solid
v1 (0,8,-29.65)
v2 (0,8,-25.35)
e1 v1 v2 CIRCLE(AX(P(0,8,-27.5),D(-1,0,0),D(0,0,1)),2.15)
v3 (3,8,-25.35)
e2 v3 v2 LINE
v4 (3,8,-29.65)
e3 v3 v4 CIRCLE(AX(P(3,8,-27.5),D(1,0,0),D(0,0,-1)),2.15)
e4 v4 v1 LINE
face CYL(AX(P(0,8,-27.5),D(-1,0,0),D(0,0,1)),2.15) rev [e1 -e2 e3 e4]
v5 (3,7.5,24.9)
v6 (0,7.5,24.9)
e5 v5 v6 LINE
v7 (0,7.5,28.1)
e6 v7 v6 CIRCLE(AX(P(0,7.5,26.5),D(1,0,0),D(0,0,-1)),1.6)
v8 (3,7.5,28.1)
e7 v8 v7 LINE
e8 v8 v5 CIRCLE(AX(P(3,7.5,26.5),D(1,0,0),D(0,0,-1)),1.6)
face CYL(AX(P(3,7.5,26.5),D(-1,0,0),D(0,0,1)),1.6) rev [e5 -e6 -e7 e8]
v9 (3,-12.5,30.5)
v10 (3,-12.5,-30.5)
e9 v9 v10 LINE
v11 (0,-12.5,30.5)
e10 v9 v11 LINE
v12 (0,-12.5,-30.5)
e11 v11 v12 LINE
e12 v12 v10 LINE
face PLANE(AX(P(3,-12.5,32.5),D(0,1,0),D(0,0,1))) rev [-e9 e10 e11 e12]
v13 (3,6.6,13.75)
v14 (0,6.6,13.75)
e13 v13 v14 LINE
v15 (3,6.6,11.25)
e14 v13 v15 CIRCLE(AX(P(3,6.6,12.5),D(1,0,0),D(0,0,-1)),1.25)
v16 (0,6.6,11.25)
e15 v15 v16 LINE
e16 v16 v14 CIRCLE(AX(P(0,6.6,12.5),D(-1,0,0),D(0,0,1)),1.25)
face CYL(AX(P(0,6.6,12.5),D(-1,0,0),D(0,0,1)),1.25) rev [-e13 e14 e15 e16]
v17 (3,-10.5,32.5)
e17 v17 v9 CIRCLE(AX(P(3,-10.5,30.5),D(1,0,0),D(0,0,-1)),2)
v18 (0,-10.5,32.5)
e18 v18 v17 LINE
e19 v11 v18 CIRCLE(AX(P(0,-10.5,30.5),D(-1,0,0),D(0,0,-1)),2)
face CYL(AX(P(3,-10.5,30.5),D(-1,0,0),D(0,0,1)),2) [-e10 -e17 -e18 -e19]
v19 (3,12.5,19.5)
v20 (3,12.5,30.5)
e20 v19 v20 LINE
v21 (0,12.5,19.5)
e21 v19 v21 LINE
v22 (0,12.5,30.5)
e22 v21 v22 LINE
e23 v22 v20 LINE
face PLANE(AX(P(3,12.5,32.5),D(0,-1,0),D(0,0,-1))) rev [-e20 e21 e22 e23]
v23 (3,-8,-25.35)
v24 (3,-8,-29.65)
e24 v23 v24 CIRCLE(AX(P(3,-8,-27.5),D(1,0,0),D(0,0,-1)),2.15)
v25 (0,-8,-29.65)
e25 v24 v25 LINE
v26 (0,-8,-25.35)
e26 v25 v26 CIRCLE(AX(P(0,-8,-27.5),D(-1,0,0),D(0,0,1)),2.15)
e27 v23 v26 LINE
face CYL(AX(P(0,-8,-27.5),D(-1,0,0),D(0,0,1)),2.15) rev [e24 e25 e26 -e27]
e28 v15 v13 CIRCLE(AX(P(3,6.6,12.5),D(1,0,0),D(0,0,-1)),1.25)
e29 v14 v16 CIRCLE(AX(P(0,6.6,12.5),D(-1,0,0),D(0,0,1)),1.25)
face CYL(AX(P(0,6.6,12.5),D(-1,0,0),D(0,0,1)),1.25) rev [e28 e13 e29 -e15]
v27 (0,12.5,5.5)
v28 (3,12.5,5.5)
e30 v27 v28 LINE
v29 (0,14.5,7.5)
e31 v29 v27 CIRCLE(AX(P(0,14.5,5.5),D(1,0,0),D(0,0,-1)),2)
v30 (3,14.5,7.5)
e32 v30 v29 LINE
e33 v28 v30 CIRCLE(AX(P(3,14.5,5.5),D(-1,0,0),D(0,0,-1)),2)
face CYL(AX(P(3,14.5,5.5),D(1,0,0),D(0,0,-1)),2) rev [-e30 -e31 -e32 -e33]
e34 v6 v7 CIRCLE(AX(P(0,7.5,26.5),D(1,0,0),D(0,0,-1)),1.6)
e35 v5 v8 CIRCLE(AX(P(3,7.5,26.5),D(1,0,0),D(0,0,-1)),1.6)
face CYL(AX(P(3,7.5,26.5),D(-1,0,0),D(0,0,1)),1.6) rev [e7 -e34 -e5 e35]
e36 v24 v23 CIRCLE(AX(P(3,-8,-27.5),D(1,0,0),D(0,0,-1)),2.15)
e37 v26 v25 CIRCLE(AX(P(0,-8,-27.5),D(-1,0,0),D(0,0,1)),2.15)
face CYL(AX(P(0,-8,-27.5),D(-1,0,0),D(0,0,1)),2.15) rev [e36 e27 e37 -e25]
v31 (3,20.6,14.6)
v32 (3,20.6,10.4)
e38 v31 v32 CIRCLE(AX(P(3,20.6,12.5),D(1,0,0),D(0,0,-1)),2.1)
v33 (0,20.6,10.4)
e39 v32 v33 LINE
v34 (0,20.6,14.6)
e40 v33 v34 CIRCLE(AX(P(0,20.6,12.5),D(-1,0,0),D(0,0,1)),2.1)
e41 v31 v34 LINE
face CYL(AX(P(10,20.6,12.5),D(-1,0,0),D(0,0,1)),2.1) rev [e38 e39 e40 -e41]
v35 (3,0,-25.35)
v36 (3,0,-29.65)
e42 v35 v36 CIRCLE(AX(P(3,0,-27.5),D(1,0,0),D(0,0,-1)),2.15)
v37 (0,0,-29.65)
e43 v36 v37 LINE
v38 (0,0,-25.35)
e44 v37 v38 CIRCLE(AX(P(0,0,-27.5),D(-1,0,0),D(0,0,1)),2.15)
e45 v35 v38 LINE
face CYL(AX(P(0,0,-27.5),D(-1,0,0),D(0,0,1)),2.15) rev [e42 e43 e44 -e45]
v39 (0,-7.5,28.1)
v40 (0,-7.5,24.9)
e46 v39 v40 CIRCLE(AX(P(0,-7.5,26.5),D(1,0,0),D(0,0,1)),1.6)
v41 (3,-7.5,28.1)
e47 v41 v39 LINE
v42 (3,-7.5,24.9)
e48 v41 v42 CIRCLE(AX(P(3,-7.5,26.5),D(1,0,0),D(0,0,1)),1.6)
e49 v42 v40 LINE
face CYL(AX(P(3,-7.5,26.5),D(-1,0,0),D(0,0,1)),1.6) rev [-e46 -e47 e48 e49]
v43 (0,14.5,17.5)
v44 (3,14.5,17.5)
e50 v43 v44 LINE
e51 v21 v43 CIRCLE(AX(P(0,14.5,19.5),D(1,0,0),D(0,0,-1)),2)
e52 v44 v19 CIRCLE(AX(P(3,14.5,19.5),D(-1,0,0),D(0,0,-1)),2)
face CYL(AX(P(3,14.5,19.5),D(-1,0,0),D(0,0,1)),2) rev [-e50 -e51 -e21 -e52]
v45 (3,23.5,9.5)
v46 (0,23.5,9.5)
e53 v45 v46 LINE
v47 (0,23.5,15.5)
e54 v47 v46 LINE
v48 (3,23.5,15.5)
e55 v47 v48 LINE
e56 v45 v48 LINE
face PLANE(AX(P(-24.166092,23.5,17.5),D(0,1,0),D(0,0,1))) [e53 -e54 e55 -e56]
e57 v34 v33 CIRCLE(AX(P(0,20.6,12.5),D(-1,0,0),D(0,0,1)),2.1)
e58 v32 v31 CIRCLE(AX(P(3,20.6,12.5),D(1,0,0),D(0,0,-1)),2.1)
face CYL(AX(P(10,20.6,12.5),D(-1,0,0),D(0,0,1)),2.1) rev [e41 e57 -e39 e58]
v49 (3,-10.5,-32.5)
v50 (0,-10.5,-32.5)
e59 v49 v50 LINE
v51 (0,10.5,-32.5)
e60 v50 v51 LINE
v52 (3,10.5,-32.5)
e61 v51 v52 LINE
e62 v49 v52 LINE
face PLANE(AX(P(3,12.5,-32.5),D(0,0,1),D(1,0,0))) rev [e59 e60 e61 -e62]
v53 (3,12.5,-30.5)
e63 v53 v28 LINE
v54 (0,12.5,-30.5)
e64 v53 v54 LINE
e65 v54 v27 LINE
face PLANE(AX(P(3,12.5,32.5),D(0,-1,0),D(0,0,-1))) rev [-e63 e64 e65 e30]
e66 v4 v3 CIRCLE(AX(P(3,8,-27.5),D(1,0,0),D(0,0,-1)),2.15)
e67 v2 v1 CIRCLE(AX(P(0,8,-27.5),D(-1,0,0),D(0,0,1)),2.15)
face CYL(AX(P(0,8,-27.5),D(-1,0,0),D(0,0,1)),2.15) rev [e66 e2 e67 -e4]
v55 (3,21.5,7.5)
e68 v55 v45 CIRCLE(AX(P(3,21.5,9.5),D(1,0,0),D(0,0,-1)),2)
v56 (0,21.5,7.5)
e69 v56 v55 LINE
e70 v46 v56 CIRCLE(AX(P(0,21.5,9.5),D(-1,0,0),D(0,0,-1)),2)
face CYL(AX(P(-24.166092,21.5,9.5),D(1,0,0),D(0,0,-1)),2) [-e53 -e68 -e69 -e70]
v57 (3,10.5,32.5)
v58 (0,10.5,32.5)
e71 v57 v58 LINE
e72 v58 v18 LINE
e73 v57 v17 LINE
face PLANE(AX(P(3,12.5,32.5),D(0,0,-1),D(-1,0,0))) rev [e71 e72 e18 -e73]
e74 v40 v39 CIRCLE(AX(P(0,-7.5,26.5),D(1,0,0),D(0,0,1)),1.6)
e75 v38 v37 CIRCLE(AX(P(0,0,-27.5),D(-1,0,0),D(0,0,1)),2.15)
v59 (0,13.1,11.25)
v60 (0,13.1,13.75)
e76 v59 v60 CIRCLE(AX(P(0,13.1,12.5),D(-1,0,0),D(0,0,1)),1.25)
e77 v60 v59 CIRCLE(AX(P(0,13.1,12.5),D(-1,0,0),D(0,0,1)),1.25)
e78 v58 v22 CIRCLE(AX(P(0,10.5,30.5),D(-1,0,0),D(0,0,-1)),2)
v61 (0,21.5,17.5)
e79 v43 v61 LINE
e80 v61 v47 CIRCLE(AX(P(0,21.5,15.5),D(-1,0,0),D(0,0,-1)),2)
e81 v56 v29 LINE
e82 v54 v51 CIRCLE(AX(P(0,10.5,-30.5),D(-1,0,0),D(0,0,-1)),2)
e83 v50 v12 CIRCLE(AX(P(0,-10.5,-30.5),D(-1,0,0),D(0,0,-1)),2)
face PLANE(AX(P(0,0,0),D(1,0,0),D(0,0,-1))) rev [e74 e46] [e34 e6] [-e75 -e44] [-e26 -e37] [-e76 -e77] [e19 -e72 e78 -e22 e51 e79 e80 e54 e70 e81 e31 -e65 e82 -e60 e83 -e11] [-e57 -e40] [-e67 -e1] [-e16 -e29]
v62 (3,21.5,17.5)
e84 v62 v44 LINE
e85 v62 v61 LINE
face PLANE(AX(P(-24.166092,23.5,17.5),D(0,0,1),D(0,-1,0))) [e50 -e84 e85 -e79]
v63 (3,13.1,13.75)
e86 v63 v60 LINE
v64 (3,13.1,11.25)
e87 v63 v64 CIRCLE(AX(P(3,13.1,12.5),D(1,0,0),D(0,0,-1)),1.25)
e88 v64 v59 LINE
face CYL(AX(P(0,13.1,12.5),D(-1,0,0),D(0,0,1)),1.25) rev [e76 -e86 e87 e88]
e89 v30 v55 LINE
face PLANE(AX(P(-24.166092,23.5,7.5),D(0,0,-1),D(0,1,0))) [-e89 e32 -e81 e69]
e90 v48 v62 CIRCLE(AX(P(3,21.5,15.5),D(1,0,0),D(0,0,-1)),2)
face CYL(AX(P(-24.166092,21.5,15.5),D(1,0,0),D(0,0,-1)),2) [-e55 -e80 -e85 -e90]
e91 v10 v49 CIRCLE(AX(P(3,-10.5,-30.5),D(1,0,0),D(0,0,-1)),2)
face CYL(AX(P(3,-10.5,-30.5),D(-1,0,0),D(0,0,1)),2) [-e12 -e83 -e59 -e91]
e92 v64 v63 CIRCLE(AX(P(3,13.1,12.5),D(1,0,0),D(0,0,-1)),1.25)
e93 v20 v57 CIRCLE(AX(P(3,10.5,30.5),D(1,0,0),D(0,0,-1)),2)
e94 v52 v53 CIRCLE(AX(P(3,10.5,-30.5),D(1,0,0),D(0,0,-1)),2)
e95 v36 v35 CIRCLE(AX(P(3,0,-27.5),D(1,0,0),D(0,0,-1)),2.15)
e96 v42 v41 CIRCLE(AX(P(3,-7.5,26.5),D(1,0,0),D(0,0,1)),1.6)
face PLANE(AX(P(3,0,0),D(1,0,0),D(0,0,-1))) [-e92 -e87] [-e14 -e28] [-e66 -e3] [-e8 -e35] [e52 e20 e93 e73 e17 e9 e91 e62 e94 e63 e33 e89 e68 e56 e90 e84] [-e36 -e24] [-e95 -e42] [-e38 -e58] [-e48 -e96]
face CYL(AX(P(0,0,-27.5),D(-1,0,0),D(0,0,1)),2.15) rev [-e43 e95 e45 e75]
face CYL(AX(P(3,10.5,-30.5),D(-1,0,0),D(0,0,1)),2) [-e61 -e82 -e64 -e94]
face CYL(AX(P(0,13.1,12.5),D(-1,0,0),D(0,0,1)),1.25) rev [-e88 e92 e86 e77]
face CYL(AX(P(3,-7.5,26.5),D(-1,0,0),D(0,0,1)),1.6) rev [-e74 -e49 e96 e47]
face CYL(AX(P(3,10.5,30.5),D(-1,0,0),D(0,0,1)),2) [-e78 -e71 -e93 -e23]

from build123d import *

# Parameters (mm, degrees)
SKETCH_1_W                  = 65
SKETCH_1_H                  = 25
SKETCH_1_R                  = 1.6
EXTRUDE_1_DEPTH             = 3
FILLET_1_R                  = 2
HOLE_WIZARD_4_3_4_3_1_D     = 4.3
HOLE_WIZARD_4_3_4_3_1_DEPTH = 11.5
HOLE_WIZARD_4_3_4_3_1_TIP   = 1.291850331
SKETCH_4_W                  = 10
SKETCH_4_H                  = 22
EXTRUDE_2_DEPTH             = 3
SKETCH_5_R                  = 2.1
CUT_EXTRUDE_1_DEPTH         = 10
FILLET_2_R                  = 2
HOLE_WIZARD_M3_1_D          = 2.5
HOLE_WIZARD_M3_1_DEPTH      = 8.5
HOLE_WIZARD_M3_1_TIP        = 0.751075774


with BuildPart() as part:
    # 草图1 → 凸台-拉伸1 (new body)
    with BuildSketch(Plane(origin=(0, 0, 0), x_dir=(0, 0, -1), z_dir=(1, 0, 0))):
        Rectangle(SKETCH_1_W, SKETCH_1_H)
        with Locations((-26.5, 7.5)):
            Circle(SKETCH_1_R, mode=Mode.SUBTRACT)
        with Locations(Location((-26.5, -7.5, 0), (0, 0, 180))):
            Circle(SKETCH_1_R, mode=Mode.SUBTRACT)
    extrude(amount=EXTRUDE_1_DEPTH)

    # 圆角1
    fillet_1_edges = [part.edges().sort_by_distance(p)[0] for p in [
        (1.5, -12.5, -32.5),
        (1.5, -12.5, 32.5),
        (1.5, 12.5, 32.5),
        (1.5, 12.5, -32.5),
    ]]
    fillet(fillet_1_edges, radius=FILLET_1_R)

    # Ø4.3 (4.3) 直径孔1
    with Locations(Plane.ZY):
        with Locations((-27.5, 8), (-27.5, -8), (-27.5, 0)):
            Hole(HOLE_WIZARD_4_3_4_3_1_D / 2, depth=HOLE_WIZARD_4_3_4_3_1_DEPTH)
            with Locations((0, 0, -(HOLE_WIZARD_4_3_4_3_1_DEPTH + HOLE_WIZARD_4_3_4_3_1_TIP / 2))):  # 118° drill point
                Cone(0, HOLE_WIZARD_4_3_4_3_1_D / 2, HOLE_WIZARD_4_3_4_3_1_TIP, mode=Mode.SUBTRACT)

    # 草图4 → 凸台-拉伸2 (add)
    with BuildSketch(Plane(origin=(3, 0, 0), x_dir=(0, 0, -1), z_dir=(1, 0, 0))):
        with Locations((-12.5, 12.5)):
            Rectangle(SKETCH_4_W, SKETCH_4_H)
    extrude(amount=-EXTRUDE_2_DEPTH)

    # 草图5 → 切除-拉伸1 (cut)
    with BuildSketch(Plane.ZY):
        with Locations((12.5, 20.6)):
            Circle(SKETCH_5_R)
    extrude(amount=-CUT_EXTRUDE_1_DEPTH, mode=Mode.SUBTRACT)

    # 圆角2
    fillet_2_edges = [part.edges().sort_by_distance(p)[0] for p in [
        (1.5, 12.5, 17.5),
        (1.5, 12.5, 7.5),
        (1.5, 23.5, 7.5),
        (1.5, 23.5, 17.5),
    ]]
    fillet(fillet_2_edges, radius=FILLET_2_R)

    # M3 螺纹孔1
    with Locations(Plane.ZY):
        with Locations((12.5, 6.6), (12.5, 13.1)):
            Hole(HOLE_WIZARD_M3_1_D / 2, depth=HOLE_WIZARD_M3_1_DEPTH)
            with Locations((0, 0, -(HOLE_WIZARD_M3_1_DEPTH + HOLE_WIZARD_M3_1_TIP / 2))):  # 118° drill point
                Cone(0, HOLE_WIZARD_M3_1_D / 2, HOLE_WIZARD_M3_1_TIP, mode=Mode.SUBTRACT)


solid = part.part
